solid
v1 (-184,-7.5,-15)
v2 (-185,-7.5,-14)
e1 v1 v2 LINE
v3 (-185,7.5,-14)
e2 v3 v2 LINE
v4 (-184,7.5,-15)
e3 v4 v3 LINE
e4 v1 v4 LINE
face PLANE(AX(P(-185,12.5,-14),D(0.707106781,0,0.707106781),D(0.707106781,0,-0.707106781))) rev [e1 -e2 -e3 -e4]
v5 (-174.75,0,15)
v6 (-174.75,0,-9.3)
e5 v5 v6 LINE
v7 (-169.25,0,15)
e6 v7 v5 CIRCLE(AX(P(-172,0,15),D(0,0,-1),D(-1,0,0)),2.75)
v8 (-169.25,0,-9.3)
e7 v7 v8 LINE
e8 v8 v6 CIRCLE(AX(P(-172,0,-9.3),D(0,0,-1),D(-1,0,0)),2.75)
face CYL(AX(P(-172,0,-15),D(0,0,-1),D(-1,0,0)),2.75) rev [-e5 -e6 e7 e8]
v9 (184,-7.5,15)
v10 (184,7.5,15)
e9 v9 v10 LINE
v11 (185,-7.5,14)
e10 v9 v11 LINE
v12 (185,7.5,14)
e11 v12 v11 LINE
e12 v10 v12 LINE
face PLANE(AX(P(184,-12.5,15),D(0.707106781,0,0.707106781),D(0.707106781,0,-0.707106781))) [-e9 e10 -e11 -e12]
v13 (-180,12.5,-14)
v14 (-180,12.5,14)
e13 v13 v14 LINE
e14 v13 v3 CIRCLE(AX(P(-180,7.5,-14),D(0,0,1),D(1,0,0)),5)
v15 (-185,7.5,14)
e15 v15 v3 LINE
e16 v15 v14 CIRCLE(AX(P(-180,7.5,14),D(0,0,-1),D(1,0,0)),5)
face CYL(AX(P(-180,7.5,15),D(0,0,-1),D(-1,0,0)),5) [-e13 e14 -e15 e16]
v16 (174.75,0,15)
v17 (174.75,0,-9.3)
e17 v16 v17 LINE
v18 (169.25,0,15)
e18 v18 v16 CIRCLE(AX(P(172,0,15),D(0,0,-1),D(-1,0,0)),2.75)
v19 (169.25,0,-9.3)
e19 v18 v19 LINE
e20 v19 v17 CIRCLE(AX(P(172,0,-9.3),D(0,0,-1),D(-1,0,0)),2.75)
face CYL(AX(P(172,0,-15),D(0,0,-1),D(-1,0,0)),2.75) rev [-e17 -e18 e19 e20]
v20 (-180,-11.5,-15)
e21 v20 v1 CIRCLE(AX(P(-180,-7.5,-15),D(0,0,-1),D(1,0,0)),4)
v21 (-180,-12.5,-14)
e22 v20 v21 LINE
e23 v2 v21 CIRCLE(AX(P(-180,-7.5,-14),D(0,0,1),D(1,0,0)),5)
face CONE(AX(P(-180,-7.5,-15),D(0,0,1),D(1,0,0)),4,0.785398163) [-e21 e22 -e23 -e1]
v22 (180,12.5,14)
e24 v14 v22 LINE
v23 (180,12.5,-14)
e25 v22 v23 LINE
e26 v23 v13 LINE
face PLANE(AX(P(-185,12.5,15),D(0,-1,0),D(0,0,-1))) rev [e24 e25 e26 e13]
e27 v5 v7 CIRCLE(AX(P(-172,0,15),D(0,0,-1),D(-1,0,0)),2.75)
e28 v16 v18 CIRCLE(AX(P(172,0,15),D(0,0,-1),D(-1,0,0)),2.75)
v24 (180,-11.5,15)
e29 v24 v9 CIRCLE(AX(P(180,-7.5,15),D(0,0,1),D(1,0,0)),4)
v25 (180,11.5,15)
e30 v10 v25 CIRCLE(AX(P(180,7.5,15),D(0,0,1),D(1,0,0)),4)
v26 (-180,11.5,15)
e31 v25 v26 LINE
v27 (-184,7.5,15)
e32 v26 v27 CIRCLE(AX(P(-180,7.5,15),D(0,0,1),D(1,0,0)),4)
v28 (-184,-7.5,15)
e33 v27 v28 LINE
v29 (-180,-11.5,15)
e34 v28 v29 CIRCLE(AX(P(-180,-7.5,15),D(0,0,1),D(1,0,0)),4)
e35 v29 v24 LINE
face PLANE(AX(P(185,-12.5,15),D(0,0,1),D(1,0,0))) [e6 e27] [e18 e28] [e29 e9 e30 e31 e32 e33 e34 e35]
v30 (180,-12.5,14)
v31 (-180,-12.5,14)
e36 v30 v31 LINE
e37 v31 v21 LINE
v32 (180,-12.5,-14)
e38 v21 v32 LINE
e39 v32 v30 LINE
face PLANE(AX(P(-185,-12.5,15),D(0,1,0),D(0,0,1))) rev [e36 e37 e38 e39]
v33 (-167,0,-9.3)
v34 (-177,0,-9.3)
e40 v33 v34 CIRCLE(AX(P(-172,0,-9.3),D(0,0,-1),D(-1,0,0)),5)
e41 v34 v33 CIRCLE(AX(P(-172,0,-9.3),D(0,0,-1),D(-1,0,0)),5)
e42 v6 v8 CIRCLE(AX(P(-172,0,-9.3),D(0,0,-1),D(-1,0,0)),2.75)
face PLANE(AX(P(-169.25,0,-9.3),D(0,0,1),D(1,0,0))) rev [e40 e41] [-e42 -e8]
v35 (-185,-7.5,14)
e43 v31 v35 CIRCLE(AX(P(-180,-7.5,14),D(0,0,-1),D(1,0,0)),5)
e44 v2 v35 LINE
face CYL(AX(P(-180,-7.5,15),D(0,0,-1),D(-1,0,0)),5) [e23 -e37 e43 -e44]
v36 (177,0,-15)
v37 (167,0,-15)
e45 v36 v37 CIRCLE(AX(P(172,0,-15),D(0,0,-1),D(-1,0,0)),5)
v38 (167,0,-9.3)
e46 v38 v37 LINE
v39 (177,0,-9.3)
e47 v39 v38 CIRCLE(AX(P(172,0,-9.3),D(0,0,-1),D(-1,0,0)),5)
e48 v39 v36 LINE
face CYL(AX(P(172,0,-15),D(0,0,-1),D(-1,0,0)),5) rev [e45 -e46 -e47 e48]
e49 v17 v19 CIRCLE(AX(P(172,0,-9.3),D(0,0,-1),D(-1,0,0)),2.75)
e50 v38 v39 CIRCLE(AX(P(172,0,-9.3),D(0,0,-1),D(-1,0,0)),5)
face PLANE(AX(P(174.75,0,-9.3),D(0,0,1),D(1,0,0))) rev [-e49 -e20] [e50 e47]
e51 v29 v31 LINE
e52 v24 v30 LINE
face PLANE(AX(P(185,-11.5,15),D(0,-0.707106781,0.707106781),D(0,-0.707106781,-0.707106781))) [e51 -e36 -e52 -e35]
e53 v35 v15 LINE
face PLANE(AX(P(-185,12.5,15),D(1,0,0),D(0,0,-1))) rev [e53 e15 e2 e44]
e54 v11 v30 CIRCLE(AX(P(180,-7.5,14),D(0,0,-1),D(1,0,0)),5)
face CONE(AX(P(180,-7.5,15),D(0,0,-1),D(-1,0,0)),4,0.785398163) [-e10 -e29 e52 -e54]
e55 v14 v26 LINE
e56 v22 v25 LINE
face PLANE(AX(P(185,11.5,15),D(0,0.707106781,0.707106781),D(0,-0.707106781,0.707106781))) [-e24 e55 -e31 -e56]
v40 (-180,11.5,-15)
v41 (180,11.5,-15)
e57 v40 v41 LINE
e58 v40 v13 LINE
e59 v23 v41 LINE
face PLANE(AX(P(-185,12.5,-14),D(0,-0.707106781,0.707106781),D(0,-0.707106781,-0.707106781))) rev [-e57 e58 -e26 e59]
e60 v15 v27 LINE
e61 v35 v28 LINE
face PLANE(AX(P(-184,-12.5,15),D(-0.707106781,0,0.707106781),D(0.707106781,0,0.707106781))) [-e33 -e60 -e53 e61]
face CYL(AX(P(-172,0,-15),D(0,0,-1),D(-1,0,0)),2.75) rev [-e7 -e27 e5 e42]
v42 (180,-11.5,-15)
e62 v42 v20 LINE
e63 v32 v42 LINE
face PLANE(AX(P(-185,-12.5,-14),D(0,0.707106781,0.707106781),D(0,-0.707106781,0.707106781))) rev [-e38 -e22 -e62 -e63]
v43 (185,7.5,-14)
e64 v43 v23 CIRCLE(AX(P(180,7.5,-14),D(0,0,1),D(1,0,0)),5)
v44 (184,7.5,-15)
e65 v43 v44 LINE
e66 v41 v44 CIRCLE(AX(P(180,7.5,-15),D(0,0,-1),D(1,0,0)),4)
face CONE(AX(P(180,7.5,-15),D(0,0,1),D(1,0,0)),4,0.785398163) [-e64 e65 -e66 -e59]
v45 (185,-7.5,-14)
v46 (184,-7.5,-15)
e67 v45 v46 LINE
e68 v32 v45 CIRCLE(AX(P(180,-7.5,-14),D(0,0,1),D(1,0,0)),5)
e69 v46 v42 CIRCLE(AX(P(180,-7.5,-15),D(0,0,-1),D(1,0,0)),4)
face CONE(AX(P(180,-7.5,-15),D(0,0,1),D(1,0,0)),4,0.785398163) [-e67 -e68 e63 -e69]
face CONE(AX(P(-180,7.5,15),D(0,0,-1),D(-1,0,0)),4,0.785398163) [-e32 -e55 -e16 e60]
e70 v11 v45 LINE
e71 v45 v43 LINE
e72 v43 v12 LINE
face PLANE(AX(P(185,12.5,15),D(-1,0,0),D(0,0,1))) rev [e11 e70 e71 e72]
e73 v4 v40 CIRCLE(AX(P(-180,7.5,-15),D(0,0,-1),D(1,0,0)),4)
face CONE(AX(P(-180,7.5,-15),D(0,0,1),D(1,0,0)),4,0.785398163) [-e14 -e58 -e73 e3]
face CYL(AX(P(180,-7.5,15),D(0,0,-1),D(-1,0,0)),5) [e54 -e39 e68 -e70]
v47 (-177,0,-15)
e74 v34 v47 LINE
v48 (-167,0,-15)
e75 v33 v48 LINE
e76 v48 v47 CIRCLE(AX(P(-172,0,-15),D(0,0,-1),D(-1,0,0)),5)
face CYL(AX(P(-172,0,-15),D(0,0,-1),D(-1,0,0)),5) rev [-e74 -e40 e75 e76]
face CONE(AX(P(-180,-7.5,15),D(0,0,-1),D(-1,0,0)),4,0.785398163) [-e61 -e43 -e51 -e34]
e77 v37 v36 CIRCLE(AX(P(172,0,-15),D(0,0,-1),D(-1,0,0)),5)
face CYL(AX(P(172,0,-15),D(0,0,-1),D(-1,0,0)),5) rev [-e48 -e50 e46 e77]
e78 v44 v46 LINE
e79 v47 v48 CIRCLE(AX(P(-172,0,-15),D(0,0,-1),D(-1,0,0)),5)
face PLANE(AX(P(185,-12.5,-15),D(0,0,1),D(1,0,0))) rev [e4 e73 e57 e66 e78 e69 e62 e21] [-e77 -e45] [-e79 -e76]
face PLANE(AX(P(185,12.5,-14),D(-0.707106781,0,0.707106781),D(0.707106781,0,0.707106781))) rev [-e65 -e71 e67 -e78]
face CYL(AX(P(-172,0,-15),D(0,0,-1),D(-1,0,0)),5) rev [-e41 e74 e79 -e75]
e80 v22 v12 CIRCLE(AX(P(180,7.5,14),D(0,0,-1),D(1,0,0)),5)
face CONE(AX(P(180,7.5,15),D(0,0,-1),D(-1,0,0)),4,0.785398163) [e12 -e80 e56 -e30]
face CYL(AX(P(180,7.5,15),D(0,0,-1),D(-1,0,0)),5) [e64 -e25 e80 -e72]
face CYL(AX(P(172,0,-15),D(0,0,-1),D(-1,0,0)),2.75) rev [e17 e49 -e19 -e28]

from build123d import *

# Parameters (mm, degrees)
SKETCH1_W                                            = 370
SKETCH1_H                                            = 25
BOSS_EXTRUDE1_DEPTH                                  = 15
FILLET1_R                                            = 5
CHAMFER1_SIZE                                        = 1
HOLE_SIZE_PER_SOCKET_HEAD_CAP_SCREW_TYPE_D           = 5.5
HOLE_SIZE_PER_SOCKET_HEAD_CAP_SCREW_TYPE_CBORE_D     = 10
HOLE_SIZE_PER_SOCKET_HEAD_CAP_SCREW_TYPE_CBORE_DEPTH = 5.7


with BuildPart() as part:
    # Sketch1 → Boss-Extrude1 (new, symmetric)
    with BuildSketch(Plane.XY):
        Rectangle(SKETCH1_W, SKETCH1_H)
    extrude(amount=BOSS_EXTRUDE1_DEPTH, both=True)

    # Fillet1
    fillet1_edges = [part.edges().sort_by_distance(p)[0] for p in [
        (185, -12.5, 0),
        (-185, -12.5, 0),
        (-185, 12.5, 0),
        (185, 12.5, 0),
    ]]
    fillet(fillet1_edges, radius=FILLET1_R)

    # Chamfer1
    chamfer1_edges = [part.edges().sort_by_distance(p)[0] for p in [
        (-185, 0, -15),
        (-185, 0, 15),
        (185, 0, -15),
        (0, -12.5, -15),
        (0, 12.5, -15),
        (183.535533906, 11.035533906, -15),
        (183.535533906, -11.035533906, -15),
        (-183.535533906, -11.035533906, -15),
        (-183.535533906, 11.035533906, -15),
        (0, 12.5, 15),
        (185, 0, 15),
        (0, -12.5, 15),
        (183.535533906, 11.035533906, 15),
        (183.535533906, -11.035533906, 15),
        (-183.535533906, -11.035533906, 15),
        (-183.535533906, 11.035533906, 15),
    ]]
    chamfer(chamfer1_edges, length=CHAMFER1_SIZE)

    # Hole size per socket head cap screw type 1 (through all)
    with Locations(Plane(origin=(0, 0, -15), x_dir=(-1, 0, 0), z_dir=(0, 0, -1))):
        with Locations((-172, 0), (172, 0)):
            CounterBoreHole(HOLE_SIZE_PER_SOCKET_HEAD_CAP_SCREW_TYPE_D / 2, HOLE_SIZE_PER_SOCKET_HEAD_CAP_SCREW_TYPE_CBORE_D / 2, HOLE_SIZE_PER_SOCKET_HEAD_CAP_SCREW_TYPE_CBORE_DEPTH)


solid = part.part
